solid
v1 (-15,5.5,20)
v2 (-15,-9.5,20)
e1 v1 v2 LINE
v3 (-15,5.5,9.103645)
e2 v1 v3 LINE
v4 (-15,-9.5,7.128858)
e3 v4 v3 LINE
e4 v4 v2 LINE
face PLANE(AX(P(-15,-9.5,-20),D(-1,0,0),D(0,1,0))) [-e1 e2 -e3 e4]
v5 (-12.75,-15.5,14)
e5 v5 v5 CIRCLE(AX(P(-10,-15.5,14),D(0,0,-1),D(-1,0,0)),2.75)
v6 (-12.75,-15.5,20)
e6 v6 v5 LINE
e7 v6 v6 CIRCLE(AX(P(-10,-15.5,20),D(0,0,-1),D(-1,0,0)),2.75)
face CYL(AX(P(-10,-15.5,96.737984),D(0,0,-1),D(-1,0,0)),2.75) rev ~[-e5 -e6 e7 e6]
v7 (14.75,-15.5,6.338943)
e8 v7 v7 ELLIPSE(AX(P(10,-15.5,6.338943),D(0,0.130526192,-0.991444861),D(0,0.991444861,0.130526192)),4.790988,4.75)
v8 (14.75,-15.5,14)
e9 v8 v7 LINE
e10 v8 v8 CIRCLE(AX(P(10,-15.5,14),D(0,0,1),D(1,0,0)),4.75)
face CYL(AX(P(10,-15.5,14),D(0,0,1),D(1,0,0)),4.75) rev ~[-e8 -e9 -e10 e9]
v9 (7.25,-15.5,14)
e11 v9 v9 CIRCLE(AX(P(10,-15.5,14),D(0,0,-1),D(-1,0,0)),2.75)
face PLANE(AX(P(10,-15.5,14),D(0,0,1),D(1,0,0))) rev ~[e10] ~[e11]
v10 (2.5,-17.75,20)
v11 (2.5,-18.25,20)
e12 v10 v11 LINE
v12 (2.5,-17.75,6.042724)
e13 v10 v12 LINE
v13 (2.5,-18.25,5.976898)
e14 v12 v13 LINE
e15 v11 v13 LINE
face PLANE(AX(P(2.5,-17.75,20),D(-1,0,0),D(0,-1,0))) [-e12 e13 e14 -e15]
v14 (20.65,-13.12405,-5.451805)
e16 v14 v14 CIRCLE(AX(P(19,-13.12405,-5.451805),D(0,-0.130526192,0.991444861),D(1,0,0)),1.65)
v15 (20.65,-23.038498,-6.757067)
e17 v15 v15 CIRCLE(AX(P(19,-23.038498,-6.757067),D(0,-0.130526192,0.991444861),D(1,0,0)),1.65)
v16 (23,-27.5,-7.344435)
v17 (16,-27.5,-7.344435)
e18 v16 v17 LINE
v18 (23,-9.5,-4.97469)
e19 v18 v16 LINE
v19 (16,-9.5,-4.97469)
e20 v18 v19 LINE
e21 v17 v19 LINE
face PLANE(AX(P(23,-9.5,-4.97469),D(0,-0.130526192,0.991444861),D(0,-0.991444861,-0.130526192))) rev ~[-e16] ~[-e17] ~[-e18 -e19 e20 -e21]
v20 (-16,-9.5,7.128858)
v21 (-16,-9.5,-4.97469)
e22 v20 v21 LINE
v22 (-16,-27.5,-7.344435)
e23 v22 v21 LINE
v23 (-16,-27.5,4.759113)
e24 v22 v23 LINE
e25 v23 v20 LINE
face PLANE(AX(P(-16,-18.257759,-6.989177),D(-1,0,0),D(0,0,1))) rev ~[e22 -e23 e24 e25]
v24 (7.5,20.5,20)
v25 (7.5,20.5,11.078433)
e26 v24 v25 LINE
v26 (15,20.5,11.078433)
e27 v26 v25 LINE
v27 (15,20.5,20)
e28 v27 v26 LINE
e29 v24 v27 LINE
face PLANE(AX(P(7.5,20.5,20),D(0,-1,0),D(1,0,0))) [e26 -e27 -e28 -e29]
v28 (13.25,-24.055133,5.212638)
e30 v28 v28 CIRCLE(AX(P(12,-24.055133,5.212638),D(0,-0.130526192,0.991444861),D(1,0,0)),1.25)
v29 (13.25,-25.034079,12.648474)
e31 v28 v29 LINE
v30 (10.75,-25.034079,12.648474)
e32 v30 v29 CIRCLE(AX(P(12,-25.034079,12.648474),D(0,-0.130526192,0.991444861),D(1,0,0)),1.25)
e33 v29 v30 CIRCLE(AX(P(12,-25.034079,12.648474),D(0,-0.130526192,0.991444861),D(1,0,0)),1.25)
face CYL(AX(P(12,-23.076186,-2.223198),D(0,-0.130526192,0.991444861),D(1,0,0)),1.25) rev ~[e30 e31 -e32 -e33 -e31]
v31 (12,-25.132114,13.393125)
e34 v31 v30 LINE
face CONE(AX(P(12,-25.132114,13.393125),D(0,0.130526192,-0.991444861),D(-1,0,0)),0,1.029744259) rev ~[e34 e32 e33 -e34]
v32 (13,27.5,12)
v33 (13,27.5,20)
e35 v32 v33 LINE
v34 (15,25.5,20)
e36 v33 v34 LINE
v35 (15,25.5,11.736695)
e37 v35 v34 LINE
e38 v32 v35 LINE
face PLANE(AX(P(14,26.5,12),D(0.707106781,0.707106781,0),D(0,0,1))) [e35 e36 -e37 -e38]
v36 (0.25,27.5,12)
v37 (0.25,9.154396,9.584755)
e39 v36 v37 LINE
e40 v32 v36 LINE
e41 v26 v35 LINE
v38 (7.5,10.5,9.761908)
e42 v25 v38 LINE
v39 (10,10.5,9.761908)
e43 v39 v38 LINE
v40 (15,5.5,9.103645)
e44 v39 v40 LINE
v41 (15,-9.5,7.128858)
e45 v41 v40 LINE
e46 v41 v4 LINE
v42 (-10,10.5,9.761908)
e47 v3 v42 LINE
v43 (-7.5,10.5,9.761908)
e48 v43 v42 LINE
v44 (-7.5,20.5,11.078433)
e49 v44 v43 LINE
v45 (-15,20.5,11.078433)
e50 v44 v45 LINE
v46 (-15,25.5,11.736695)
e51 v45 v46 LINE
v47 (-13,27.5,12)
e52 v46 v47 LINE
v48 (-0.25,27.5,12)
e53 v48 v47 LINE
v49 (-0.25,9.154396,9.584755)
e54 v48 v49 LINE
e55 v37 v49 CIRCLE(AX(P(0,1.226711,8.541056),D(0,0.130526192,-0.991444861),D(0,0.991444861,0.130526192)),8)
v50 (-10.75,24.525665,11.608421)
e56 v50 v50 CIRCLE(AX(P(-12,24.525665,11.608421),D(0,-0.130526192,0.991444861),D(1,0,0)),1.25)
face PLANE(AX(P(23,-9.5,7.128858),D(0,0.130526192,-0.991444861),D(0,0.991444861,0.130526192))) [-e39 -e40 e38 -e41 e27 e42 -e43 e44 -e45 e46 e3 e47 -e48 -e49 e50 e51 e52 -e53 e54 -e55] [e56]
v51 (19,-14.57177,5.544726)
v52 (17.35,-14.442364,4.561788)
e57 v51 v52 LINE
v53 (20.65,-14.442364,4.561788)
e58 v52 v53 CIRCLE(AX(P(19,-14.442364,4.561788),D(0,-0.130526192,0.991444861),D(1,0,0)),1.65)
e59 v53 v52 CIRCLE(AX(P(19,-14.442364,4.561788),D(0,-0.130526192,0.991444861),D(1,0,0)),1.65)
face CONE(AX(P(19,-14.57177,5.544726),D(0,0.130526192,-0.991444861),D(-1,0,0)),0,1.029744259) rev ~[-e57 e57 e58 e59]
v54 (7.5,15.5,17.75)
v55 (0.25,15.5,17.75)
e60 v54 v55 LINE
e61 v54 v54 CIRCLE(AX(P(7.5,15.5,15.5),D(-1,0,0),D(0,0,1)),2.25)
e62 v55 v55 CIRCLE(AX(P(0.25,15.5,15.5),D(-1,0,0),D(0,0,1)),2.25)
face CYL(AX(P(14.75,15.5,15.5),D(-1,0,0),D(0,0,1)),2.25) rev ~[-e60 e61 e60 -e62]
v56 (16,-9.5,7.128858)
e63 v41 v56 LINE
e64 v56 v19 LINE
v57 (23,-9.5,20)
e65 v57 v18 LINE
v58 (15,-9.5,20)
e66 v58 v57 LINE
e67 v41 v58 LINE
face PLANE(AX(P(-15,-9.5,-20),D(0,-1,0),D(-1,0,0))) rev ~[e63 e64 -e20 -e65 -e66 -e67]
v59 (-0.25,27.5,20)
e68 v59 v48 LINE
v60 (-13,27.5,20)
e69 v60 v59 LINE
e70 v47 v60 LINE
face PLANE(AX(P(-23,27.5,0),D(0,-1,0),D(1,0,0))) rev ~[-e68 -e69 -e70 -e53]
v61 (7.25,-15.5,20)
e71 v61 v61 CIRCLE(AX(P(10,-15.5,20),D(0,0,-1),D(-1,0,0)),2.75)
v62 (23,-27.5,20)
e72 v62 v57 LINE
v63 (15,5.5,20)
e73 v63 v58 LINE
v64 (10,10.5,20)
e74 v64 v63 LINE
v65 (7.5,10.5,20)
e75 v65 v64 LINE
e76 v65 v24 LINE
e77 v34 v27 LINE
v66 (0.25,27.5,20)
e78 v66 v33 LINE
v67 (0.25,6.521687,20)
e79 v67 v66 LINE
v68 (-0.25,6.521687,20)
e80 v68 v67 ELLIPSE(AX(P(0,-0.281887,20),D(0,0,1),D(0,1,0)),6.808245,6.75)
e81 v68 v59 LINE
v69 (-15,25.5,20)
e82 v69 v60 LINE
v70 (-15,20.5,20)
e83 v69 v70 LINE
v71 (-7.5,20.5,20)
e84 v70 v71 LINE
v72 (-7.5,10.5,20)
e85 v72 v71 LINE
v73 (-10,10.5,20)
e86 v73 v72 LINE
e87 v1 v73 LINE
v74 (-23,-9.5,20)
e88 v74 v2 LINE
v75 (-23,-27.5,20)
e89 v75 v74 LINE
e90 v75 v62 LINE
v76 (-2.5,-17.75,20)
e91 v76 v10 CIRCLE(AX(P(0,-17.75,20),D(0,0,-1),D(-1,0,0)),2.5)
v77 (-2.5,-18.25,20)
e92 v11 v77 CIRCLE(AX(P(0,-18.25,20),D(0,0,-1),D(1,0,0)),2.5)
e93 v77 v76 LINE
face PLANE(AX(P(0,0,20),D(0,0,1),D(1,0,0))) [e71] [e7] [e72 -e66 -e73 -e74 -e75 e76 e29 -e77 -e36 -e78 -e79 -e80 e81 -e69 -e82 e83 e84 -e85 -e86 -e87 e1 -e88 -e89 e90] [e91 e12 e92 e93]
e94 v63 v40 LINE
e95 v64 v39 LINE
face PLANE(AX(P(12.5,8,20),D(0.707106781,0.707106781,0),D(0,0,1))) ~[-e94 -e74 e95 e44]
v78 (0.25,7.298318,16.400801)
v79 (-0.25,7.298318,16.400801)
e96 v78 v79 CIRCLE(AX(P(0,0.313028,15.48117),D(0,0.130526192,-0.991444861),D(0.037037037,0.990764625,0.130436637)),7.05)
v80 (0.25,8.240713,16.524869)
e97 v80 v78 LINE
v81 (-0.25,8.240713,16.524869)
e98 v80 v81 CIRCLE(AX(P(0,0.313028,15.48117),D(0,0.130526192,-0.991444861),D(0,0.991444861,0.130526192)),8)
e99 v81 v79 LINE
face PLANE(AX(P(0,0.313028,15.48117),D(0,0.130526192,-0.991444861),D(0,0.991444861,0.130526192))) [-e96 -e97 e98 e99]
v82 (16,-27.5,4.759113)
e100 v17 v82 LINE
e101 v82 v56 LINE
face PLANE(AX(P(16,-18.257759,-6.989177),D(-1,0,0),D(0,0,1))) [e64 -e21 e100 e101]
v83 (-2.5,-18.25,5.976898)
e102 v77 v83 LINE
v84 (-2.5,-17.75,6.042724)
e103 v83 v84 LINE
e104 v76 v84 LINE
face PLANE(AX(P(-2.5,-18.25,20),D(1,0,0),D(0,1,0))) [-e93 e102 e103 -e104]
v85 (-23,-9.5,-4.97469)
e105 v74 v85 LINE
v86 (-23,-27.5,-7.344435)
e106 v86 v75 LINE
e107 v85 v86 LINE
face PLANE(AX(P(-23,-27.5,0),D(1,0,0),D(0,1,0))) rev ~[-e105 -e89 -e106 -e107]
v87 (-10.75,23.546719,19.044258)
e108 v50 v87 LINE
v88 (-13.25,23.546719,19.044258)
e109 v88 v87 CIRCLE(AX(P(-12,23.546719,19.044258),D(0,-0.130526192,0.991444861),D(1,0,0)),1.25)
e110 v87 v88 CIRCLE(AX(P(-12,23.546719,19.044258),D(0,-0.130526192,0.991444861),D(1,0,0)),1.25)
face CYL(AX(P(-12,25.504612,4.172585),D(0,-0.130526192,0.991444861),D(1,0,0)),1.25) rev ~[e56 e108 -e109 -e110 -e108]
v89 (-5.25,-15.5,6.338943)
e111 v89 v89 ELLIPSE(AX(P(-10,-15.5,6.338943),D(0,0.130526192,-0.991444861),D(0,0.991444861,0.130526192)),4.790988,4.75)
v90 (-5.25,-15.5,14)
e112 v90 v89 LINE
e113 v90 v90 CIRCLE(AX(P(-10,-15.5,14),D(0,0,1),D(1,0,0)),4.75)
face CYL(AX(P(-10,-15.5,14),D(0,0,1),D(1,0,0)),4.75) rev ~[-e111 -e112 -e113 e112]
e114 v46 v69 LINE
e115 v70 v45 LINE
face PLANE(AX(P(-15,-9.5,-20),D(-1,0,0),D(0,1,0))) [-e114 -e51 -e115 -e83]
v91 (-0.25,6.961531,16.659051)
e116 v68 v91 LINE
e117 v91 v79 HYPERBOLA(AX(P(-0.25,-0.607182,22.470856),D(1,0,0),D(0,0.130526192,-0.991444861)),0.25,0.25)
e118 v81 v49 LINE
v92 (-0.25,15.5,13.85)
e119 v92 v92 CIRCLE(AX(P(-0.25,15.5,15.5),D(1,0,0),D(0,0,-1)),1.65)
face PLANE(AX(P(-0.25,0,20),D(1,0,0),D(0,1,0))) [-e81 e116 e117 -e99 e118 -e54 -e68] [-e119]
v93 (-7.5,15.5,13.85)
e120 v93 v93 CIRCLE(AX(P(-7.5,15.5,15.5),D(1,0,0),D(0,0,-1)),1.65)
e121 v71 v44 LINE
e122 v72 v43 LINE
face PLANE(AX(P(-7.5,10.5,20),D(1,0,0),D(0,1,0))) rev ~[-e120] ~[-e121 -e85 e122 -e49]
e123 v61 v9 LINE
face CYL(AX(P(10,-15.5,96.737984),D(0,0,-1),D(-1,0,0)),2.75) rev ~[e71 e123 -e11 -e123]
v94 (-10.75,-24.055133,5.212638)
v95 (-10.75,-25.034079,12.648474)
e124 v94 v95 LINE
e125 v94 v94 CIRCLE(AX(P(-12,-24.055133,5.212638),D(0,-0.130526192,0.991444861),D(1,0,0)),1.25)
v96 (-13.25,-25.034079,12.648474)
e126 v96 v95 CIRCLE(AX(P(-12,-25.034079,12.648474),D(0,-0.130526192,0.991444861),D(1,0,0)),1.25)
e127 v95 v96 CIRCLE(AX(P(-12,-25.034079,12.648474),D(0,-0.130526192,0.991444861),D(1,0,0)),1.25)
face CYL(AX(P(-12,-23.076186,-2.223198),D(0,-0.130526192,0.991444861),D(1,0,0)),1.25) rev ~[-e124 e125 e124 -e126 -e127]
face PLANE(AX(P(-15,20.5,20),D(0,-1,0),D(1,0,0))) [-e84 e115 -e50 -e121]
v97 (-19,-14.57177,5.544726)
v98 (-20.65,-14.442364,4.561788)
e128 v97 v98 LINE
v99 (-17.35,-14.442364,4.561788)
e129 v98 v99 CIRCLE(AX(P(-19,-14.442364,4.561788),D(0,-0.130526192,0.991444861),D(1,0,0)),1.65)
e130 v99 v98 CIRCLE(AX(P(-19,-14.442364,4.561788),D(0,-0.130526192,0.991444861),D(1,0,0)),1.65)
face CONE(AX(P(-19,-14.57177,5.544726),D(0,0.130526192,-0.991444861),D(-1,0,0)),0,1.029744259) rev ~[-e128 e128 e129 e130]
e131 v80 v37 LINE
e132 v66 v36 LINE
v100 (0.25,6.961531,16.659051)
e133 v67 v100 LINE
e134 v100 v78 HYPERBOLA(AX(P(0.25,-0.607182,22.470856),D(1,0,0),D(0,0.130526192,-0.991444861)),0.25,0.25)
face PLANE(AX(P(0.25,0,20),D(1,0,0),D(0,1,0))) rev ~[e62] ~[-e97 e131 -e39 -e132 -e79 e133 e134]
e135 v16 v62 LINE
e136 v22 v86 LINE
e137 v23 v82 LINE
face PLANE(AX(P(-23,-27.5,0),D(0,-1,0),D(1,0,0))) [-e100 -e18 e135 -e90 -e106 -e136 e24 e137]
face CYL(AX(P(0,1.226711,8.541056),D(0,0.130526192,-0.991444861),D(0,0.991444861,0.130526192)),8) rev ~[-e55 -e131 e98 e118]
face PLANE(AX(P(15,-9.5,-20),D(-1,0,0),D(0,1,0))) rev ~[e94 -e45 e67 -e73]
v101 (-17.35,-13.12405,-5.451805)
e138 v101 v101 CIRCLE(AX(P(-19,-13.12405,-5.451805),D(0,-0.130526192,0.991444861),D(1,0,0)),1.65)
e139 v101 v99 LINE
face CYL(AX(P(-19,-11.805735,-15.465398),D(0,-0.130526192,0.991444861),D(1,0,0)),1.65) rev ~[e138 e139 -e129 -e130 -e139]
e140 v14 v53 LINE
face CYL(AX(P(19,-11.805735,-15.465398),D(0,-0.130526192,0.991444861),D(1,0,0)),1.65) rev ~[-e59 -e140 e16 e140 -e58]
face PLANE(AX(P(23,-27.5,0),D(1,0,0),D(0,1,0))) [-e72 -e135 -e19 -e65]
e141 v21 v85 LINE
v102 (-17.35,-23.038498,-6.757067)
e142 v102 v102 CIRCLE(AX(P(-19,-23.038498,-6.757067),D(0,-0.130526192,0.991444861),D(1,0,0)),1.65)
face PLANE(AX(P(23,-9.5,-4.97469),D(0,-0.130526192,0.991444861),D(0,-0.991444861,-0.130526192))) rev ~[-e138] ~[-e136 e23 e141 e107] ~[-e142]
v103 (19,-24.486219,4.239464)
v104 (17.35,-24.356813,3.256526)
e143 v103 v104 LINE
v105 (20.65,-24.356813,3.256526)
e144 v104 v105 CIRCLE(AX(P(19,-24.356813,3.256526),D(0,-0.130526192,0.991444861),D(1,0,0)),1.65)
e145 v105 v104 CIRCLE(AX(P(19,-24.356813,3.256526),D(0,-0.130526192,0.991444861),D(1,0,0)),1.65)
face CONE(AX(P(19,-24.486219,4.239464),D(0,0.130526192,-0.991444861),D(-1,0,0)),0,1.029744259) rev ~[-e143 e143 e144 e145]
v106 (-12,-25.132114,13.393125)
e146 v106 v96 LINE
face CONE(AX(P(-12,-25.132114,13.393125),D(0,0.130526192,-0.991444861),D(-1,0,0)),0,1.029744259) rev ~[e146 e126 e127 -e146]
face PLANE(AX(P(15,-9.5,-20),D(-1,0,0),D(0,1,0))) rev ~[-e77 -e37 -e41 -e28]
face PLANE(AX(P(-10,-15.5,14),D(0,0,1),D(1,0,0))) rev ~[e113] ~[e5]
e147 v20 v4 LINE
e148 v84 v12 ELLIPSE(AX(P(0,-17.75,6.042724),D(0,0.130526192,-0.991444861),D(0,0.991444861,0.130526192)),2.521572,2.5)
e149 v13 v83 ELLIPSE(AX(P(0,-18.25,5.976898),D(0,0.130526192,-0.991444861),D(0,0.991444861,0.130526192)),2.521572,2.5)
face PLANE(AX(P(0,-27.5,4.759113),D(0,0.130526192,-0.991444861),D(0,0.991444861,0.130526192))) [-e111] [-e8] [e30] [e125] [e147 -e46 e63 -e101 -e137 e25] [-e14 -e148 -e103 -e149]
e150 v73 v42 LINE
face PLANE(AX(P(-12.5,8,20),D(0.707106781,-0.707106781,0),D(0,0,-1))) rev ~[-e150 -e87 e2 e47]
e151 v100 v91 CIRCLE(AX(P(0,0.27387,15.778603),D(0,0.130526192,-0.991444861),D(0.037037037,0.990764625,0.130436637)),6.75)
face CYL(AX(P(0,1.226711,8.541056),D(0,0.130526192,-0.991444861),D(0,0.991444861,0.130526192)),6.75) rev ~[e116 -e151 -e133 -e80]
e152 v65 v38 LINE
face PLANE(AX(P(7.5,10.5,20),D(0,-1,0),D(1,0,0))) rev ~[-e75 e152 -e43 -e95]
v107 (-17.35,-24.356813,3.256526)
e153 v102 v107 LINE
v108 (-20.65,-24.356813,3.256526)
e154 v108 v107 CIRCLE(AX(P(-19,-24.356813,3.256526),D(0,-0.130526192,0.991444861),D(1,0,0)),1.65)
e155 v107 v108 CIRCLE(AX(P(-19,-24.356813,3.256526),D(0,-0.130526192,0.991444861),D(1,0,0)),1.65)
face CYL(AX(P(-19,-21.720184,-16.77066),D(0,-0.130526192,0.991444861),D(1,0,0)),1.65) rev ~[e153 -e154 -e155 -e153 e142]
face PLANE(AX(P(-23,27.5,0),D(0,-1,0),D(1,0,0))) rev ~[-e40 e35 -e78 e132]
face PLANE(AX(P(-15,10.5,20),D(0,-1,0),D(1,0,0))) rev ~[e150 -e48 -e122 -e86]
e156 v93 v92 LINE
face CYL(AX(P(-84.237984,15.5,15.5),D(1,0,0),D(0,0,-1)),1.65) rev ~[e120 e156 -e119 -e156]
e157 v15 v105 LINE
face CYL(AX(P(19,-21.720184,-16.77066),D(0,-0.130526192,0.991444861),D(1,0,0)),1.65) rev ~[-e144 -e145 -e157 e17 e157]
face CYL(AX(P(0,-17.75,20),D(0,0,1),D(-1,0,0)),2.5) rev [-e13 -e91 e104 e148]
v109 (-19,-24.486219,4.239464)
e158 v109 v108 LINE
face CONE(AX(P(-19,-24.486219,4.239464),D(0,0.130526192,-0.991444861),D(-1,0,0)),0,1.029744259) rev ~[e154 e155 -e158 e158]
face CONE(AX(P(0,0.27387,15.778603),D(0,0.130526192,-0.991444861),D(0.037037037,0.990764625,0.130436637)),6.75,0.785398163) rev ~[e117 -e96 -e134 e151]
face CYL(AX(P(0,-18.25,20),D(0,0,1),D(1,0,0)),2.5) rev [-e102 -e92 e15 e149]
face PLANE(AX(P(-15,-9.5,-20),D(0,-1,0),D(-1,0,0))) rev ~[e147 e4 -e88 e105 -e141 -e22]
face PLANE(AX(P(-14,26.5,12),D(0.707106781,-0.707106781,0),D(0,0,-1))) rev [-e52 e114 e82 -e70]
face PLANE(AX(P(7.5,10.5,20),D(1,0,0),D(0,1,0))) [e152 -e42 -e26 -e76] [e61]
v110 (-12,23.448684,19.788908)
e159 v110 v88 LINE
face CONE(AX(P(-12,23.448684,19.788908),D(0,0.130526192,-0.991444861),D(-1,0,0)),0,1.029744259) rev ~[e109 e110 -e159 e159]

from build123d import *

# Parameters (mm, degrees)
SKETCH1_W                      = 46
SKETCH1_H                      = 55
BOSS_EXTRUDE1_DEPTH            = 20
CUT_EXTRUDE1_DEPTH             = 58.203583804
SKETCH3_R                      = 6.75
CUT_EXTRUDE2_DEPTH             = 47.296696276
SKETCH4_R                      = 2.5
CUT_EXTRUDE3_DEPTH             = 54.714523176
SKETCH6_W                      = 8
SKETCH6_H                      = 37
CUT_EXTRUDE4_DEPTH             = 54.714523176
CUT_EXTRUDE5_DEPTH             = 16
CUT_EXTRUDE6_DEPTH             = 58.203583804
SKETCH9_R                      = 8
CUT_EXTRUDE7_DEPTH             = 7
CHAMFER1_SIZE                  = 2
F_5_5_5_5_DIAMETER_HOLE1_D     = 5.5
SKETCH12_R                     = 4.75
CUT_EXTRUDE8_DEPTH             = 42.723313638
M3_TAPPED_HOLE2_D              = 2.5
M3_TAPPED_HOLE2_DEPTH          = 7.5
M3_TAPPED_HOLE2_TIP            = 0.751075774
SKETCH17_W                     = 0.5
SKETCH17_H                     = 27.5
CUT_EXTRUDE9_DEPTH             = 46.088447741
SKETCH18_W                     = 7.5
SKETCH18_H                     = 10
CUT_EXTRUDE10_DEPTH            = 46.088447741
F_4_5_4_5_DIAMETER_HOLE1_D     = 4.5
F_4_5_4_5_DIAMETER_HOLE1_DEPTH = 7.25
M4_TAPPED_HOLE1_D              = 3.3
M4_TAPPED_HOLE2_D              = 3.3
M4_TAPPED_HOLE2_DEPTH          = 10.1
M4_TAPPED_HOLE2_TIP            = 0.991420021
CHAMFER3_SIZE                  = 5
CHAMFER4_SIZE                  = 0.3
CUT_EXTRUDE11_DEPTH            = 46.088447741


with BuildPart() as part:
    # Sketch1 → Boss-Extrude1 (new, symmetric)
    with BuildSketch(Plane.XY):
        Rectangle(SKETCH1_W, SKETCH1_H)
    extrude(amount=BOSS_EXTRUDE1_DEPTH, both=True)

    # Sketch2 → Cut-Extrude1 (cut, through all)
    with BuildSketch(Plane(origin=(23, 0, 0), x_dir=(0, 0, -1), z_dir=(1, 0, 0))):
        Polygon((-12, 27.5), (20, 27.5), (20, -9.5), (-7.128857589, -9.5), align=None)
    extrude(amount=-CUT_EXTRUDE1_DEPTH, mode=Mode.SUBTRACT)

    # Sketch3 → Cut-Extrude2 (cut, through all)
    with BuildSketch(Plane(origin=(0, -1.084394382, 8.236793088), x_dir=(-1, 0, 0), z_dir=(0, 0.13052619222004844, -0.9914448613738109))):
        with Locations(Location((0, 2.331047994, 0), (0, 0, 90))):
            Circle(SKETCH3_R)
    extrude(amount=-CUT_EXTRUDE2_DEPTH, mode=Mode.SUBTRACT)

    # Sketch4 → Cut-Extrude3 (cut, through all)
    with BuildSketch(Plane.XY.offset(20)):
        with Locations((0, -18)):
            Circle(SKETCH4_R)
    extrude(amount=-CUT_EXTRUDE3_DEPTH, mode=Mode.SUBTRACT)

    # Sketch6 → Cut-Extrude4 (cut, through all)
    with BuildSketch(Plane(origin=(0, 0, -20), x_dir=(-1, 0, 0), z_dir=(0, 0, -1))):
        with Locations((-19, 9)):
            Rectangle(SKETCH6_W, SKETCH6_H)
        with Locations((19, 9)):
            Rectangle(SKETCH6_W, SKETCH6_H)
    extrude(amount=-CUT_EXTRUDE4_DEPTH, mode=Mode.SUBTRACT)

    # Sketch7 → Cut-Extrude5 (cut, symmetric)
    with BuildSketch(Plane(origin=(0, 0, 0), x_dir=(0, 0, -1), z_dir=(1, 0, 0))):
        Polygon((-7.128857589, -9.5), (20, -9.5), (20, -27.5), (-4.759112633, -27.5), align=None)
    extrude(amount=CUT_EXTRUDE5_DEPTH, both=True, mode=Mode.SUBTRACT)

    # Sketch8 → Cut-Extrude6 (cut, through all)
    with BuildSketch(Plane(origin=(23, 0, 0), x_dir=(0, 0, -1), z_dir=(1, 0, 0))):
        Polygon((4.974689938, -9.5), (7.344434894, -27.5), (20, -27.5), (20, -9.5), align=None)
    extrude(amount=-CUT_EXTRUDE6_DEPTH, mode=Mode.SUBTRACT)

    # Sketch9 → Cut-Extrude7 (cut)
    with BuildSketch(Plane(origin=(0, -1.084394382, 8.236793088), x_dir=(-1, 0, 0), z_dir=(0, 0.13052619222004838, -0.9914448613738109))):
        with Locations(Location((0, 2.331047994, 0), (0, 0, 90))):
            Circle(SKETCH9_R)
    extrude(amount=-CUT_EXTRUDE7_DEPTH, mode=Mode.SUBTRACT)

    # Chamfer1
    chamfer1_edges = [part.edges().sort_by_distance(p)[0] for p in [
        (15, 27.5, 16),
        (-15, 27.5, 16),
    ]]
    chamfer(chamfer1_edges, length=CHAMFER1_SIZE)

    # Ø5.5 (5.5) Diameter Hole1 (through all)
    with Locations(Plane.XY.offset(20)):
        with Locations((-10, -15.5), (10, -15.5)):
            Hole(F_5_5_5_5_DIAMETER_HOLE1_D / 2)

    # Sketch12 → Cut-Extrude8 (cut, through all)
    with BuildSketch(Plane.XY.offset(14)):
        with Locations((-10, -15.5)):
            Circle(SKETCH12_R)
        with Locations((10, -15.5)):
            Circle(SKETCH12_R)
    extrude(amount=-CUT_EXTRUDE8_DEPTH, mode=Mode.SUBTRACT)

    # M3 Tapped Hole2
    with Locations(Plane(origin=(0, -1.084394382, 8.236793088), x_dir=(-1, 0, 0), z_dir=(0, 0.13052619222004838, -0.9914448613738109))):
        with Locations((12, 25.831047994), (12, -23.168952006), (-12, -23.168952006)):
            Hole(M3_TAPPED_HOLE2_D / 2, depth=M3_TAPPED_HOLE2_DEPTH)
            with Locations((0, 0, -(M3_TAPPED_HOLE2_DEPTH + M3_TAPPED_HOLE2_TIP / 2))):  # 118° drill point
                Cone(0, M3_TAPPED_HOLE2_D / 2, M3_TAPPED_HOLE2_TIP, mode=Mode.SUBTRACT)

    # Sketch17 → Cut-Extrude9 (cut, through all)
    with BuildSketch(Plane.XY.offset(20)):
        with Locations((0, 13.75)):
            Rectangle(SKETCH17_W, SKETCH17_H)
    extrude(amount=-CUT_EXTRUDE9_DEPTH, mode=Mode.SUBTRACT)

    # Sketch18 → Cut-Extrude10 (cut, through all)
    with BuildSketch(Plane.XY.offset(20)):
        with Locations((-11.25, 15.5)):
            Rectangle(SKETCH18_W, SKETCH18_H)
        with Locations((11.25, 15.5)):
            Rectangle(SKETCH18_W, SKETCH18_H)
    extrude(amount=-CUT_EXTRUDE10_DEPTH, mode=Mode.SUBTRACT)

    # Ø4.5 (4.5) Diameter Hole1
    with Locations(Plane(origin=(7.5, 0, 0), x_dir=(0, 0, -1), z_dir=(1, 0, 0))):
        with Locations((-15.5, 15.5)):
            Hole(F_4_5_4_5_DIAMETER_HOLE1_D / 2, depth=F_4_5_4_5_DIAMETER_HOLE1_DEPTH)

    # M4 Tapped Hole1 (through all)
    with Locations(Plane.ZY.offset(7.5)):
        with Locations((15.5, 15.5)):
            Hole(M4_TAPPED_HOLE1_D / 2)

    # M4 Tapped Hole2
    with Locations(Plane(origin=(0, 0.481919925, -3.660545249), x_dir=(-1, 0, 0), z_dir=(0, 0.13052619222004835, -0.9914448613738109))):
        with Locations((-19, -13.723374809), (-19, -23.723374809), (19, -23.723374809), (19, -13.723374809)):
            Hole(M4_TAPPED_HOLE2_D / 2, depth=M4_TAPPED_HOLE2_DEPTH)
            with Locations((0, 0, -(M4_TAPPED_HOLE2_DEPTH + M4_TAPPED_HOLE2_TIP / 2))):  # 118° drill point
                Cone(0, M4_TAPPED_HOLE2_D / 2, M4_TAPPED_HOLE2_TIP, mode=Mode.SUBTRACT)

    # Chamfer3
    chamfer3_edges = [part.edges().sort_by_distance(p)[0] for p in [
        (-15, 10.5, 14.880953771),
        (15, 10.5, 14.880953771),
    ]]
    chamfer(chamfer3_edges, length=CHAMFER3_SIZE)

    # Chamfer4
    chamfer4_edges = [part.edges().sort_by_distance(p)[0] for p in [
        (0, -6.379224986, 14.600118138),
    ]]
    chamfer(chamfer4_edges, length=CHAMFER4_SIZE)

    # Sketch25 → Cut-Extrude11 (cut, through all)
    with BuildSketch(Plane.XY.offset(20)):
        with BuildLine():
            Line((2.5, -17.75), (2.5, -18.25))
            ThreePointArc((2.5, -18.25), (0, -20.75), (-2.5, -18.25))
            Line((-2.5, -18.25), (-2.5, -17.75))
            ThreePointArc((-2.5, -17.75), (0, -15.25), (2.5, -17.75))
        make_face()
    extrude(amount=-CUT_EXTRUDE11_DEPTH, mode=Mode.SUBTRACT)


solid = part.part
